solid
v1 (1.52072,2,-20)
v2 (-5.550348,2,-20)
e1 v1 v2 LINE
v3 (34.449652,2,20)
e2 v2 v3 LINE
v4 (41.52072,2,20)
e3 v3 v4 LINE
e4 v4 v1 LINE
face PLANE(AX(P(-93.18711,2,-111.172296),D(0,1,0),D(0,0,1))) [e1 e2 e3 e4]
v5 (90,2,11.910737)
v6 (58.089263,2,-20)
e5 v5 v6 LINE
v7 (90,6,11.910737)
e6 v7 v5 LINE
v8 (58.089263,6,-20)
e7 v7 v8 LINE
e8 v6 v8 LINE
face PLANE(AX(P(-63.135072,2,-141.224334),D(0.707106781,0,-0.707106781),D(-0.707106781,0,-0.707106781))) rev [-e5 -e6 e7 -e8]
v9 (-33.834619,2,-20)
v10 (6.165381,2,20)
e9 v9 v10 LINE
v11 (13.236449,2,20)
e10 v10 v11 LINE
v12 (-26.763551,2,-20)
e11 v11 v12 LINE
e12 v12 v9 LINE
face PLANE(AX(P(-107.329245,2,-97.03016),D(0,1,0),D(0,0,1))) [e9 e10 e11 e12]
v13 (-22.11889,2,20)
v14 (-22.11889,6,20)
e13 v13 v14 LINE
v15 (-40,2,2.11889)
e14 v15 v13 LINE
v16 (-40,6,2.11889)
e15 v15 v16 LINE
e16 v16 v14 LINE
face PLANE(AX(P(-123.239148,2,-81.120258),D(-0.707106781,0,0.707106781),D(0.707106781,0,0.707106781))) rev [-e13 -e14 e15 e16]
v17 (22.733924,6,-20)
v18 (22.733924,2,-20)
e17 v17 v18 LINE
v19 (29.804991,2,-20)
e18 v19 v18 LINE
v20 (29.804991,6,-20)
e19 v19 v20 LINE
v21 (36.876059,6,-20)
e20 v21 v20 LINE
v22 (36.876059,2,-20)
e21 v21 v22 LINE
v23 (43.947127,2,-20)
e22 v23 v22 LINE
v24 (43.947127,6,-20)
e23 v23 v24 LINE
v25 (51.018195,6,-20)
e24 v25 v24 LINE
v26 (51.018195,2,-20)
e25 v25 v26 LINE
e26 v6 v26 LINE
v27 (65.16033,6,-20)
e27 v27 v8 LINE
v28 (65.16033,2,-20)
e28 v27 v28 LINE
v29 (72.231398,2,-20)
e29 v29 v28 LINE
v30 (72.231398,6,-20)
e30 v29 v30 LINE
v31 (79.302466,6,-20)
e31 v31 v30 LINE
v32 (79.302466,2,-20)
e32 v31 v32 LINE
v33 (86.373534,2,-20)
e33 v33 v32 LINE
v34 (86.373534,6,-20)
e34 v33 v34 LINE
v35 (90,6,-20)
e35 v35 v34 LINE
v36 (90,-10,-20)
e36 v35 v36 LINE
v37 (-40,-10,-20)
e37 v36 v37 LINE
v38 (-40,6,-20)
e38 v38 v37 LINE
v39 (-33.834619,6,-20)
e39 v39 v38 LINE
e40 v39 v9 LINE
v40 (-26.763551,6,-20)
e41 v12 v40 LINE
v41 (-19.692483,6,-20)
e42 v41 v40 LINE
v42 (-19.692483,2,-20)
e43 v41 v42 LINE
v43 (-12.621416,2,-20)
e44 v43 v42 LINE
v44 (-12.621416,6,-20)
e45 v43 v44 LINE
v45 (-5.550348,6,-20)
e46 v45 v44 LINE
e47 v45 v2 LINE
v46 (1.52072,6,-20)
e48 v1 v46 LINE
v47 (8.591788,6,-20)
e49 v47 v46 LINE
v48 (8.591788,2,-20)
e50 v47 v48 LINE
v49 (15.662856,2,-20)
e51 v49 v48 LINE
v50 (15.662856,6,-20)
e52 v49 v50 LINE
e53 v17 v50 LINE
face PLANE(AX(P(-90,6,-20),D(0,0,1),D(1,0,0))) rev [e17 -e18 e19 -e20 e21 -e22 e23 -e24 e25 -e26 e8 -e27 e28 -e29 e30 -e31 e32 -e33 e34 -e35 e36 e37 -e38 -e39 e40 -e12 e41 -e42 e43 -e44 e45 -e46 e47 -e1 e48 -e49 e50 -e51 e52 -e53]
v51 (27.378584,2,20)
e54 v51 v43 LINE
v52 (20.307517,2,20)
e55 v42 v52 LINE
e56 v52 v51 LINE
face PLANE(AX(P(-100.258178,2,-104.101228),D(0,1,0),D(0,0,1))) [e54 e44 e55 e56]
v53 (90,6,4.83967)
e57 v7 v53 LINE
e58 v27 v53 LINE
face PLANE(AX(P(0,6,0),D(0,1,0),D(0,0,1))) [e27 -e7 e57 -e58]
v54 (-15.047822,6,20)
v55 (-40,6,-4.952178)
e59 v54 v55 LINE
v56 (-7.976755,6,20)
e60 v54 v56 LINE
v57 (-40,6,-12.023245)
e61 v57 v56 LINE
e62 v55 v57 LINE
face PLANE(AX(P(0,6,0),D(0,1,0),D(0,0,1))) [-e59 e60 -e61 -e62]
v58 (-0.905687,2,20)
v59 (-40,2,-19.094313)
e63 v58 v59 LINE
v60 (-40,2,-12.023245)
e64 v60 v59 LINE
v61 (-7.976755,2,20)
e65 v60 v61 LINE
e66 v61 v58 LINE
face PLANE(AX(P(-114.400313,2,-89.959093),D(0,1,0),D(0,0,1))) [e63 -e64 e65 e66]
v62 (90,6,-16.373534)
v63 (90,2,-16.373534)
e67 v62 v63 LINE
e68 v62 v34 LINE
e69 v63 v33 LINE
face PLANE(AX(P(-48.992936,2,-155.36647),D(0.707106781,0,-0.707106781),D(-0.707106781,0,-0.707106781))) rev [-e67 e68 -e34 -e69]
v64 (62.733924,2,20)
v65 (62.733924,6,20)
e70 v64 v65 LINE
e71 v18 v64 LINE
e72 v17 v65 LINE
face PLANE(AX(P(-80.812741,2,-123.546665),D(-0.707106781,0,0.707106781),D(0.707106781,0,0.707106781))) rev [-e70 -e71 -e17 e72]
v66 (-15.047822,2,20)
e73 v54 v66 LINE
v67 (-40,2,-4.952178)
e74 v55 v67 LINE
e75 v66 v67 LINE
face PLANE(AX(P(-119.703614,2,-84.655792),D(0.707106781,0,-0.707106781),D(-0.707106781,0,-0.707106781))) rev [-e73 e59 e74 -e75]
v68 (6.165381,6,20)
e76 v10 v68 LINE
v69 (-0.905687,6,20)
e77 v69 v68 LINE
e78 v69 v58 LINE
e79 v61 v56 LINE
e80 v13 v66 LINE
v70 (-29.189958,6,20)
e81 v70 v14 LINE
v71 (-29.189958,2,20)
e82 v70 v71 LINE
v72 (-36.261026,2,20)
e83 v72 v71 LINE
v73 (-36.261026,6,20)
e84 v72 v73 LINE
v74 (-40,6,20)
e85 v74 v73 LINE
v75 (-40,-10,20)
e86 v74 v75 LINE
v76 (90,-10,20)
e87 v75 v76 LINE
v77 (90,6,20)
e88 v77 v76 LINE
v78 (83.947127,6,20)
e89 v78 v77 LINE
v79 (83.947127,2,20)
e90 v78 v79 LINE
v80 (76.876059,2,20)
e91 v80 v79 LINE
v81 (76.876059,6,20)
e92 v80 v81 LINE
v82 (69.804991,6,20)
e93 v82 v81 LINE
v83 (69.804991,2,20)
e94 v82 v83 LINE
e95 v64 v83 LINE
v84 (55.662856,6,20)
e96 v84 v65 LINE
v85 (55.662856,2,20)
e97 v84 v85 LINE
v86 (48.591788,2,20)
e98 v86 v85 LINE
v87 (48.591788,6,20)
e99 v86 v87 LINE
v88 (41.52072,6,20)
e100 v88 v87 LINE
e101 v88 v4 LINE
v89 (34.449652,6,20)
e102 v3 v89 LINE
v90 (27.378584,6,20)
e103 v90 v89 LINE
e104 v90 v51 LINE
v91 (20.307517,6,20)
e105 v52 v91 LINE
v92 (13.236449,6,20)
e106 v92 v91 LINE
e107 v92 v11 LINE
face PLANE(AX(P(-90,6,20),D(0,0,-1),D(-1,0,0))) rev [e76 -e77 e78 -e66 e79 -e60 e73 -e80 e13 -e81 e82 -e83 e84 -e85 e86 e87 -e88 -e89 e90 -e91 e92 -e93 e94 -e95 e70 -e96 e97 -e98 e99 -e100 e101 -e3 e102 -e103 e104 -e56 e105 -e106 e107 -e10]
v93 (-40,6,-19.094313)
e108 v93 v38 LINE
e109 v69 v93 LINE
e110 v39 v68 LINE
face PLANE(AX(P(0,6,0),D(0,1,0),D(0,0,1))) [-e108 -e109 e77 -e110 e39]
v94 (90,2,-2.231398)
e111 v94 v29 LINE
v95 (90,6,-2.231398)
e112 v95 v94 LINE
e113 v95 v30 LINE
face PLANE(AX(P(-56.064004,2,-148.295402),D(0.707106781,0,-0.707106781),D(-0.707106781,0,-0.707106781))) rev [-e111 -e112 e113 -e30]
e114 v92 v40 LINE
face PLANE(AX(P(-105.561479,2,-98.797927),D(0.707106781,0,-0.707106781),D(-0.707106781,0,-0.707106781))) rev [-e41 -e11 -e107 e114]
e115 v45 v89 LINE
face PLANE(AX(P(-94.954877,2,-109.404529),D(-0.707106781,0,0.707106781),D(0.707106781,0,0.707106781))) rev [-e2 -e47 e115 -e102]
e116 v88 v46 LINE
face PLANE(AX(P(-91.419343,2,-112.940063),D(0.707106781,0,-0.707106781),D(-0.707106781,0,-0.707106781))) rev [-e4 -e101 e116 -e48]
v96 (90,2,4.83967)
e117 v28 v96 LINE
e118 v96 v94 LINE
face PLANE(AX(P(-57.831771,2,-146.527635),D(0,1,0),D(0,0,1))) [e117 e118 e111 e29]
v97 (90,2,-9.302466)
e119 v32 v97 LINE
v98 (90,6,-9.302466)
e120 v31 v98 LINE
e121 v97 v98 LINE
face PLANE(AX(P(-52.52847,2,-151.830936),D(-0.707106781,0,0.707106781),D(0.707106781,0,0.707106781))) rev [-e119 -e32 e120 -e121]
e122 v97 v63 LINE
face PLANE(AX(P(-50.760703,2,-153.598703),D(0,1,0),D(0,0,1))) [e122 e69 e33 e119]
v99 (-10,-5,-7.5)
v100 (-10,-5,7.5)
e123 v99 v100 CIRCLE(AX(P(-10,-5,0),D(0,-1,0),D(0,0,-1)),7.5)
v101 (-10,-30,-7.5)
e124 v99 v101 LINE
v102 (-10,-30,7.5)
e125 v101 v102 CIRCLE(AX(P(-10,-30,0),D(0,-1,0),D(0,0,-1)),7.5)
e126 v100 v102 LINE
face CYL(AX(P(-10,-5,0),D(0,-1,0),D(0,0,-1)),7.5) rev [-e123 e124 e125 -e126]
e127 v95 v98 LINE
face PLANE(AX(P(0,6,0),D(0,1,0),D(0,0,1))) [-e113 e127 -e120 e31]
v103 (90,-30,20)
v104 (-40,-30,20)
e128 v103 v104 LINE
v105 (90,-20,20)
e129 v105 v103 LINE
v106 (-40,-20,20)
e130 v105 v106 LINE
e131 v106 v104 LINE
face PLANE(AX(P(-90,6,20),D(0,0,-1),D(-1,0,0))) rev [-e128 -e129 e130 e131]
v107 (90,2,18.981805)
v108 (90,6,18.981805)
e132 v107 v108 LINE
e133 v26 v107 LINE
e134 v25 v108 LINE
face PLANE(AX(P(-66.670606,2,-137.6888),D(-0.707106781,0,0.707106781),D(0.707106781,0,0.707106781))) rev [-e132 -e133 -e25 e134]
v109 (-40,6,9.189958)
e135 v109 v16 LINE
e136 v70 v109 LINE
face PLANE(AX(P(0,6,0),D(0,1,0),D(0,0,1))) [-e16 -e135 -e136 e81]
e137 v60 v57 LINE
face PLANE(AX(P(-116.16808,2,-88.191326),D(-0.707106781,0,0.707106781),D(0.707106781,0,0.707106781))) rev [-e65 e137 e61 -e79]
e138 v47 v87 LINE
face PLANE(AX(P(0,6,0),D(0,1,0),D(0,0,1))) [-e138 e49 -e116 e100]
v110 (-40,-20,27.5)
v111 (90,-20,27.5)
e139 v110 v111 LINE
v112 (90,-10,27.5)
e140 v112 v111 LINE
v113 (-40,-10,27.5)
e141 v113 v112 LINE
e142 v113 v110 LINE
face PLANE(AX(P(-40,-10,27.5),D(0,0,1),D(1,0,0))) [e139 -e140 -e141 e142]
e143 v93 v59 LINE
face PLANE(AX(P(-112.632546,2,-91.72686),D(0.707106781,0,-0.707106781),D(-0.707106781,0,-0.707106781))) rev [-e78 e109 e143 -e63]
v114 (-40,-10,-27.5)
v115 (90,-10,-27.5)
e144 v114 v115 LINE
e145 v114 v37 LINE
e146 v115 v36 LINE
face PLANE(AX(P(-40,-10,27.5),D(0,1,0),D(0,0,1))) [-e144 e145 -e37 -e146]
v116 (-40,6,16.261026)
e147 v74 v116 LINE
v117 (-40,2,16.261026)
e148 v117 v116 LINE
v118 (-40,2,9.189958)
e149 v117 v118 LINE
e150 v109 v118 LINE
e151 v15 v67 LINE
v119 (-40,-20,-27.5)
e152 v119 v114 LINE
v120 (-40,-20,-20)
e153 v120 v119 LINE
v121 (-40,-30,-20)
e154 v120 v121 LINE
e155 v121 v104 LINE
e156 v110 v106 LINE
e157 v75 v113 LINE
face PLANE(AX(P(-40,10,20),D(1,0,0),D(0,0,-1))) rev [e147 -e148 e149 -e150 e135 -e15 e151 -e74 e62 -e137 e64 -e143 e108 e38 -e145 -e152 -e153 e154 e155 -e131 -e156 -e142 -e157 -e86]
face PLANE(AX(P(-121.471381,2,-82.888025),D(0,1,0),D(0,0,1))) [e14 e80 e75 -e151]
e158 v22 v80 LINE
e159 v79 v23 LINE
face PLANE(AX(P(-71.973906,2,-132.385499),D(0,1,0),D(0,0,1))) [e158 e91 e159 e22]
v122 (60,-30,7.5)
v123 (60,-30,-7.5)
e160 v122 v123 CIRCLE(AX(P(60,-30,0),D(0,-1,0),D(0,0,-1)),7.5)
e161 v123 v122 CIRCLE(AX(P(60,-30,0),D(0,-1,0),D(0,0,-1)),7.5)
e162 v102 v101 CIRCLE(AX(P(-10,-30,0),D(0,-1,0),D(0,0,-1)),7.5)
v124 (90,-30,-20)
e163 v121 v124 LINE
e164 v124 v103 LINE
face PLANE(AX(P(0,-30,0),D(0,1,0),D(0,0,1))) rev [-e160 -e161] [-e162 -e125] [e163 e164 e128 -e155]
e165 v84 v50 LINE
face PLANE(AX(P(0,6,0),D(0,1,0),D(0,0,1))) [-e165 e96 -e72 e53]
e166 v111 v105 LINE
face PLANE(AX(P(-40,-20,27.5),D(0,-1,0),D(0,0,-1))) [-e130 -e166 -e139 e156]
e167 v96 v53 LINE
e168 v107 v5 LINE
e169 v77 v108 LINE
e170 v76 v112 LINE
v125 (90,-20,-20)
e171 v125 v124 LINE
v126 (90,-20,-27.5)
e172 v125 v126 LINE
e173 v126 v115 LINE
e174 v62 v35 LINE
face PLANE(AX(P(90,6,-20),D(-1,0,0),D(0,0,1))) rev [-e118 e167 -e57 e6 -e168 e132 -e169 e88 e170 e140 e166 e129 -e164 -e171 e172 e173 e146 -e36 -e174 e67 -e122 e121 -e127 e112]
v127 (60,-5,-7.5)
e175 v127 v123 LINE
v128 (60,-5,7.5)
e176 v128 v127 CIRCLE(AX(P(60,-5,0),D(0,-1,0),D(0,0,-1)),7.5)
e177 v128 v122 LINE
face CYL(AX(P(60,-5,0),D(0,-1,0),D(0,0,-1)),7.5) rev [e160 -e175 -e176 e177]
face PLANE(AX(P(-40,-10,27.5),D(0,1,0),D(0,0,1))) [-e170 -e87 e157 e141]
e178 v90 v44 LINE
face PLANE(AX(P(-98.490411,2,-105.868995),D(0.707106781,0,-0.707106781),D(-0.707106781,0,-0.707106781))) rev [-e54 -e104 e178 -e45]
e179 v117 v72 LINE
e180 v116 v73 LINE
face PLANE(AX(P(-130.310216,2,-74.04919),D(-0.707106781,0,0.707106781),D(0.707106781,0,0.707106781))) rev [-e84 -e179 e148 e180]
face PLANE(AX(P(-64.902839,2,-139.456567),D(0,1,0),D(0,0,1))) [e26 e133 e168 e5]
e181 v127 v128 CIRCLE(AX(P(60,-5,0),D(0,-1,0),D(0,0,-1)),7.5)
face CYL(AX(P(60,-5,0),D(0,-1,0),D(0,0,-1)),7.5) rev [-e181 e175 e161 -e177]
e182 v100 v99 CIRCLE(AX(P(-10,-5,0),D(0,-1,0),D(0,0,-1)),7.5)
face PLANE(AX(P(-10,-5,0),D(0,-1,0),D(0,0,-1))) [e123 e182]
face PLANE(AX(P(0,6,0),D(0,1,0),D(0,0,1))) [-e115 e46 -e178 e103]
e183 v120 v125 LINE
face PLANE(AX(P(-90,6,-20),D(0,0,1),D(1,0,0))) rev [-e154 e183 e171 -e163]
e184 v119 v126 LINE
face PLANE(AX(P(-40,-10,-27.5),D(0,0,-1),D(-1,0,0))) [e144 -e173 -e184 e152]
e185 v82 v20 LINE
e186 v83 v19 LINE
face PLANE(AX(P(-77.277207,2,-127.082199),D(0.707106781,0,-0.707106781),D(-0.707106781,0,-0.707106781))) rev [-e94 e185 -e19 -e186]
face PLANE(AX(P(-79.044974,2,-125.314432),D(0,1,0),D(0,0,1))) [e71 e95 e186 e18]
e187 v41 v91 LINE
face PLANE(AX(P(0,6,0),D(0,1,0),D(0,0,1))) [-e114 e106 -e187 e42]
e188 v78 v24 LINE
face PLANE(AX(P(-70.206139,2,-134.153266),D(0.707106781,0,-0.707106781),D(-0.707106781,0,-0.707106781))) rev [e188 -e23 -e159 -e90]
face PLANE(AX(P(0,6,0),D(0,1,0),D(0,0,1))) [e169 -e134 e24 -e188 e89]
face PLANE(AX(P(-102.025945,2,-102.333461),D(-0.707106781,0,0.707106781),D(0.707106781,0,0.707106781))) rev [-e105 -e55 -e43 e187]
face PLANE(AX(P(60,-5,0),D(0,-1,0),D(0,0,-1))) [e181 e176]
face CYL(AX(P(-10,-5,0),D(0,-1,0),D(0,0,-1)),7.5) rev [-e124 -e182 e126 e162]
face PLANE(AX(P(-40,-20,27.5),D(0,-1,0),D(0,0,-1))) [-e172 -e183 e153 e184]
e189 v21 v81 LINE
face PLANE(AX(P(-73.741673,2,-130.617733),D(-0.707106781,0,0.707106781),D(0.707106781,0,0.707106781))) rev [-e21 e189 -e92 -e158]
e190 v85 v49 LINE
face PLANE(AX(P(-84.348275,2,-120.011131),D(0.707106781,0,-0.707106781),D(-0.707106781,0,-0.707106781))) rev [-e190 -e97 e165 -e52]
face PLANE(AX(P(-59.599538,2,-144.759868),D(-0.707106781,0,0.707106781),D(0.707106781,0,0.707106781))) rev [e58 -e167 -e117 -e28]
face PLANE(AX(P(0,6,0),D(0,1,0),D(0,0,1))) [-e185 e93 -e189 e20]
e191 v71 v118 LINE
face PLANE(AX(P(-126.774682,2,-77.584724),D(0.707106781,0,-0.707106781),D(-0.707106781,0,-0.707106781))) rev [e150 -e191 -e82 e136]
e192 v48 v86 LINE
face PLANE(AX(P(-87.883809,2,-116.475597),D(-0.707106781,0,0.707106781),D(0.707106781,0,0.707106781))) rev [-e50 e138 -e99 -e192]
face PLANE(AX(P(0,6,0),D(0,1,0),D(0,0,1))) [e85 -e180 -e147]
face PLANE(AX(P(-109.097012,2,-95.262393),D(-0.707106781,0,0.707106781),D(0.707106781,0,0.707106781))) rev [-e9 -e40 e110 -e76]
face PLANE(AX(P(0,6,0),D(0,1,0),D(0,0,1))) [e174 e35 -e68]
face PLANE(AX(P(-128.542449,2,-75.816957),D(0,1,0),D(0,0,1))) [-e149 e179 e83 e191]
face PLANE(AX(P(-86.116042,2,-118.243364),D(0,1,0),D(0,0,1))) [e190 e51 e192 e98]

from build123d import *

# Parameters (mm, degrees)
SKETCH1_W           = 180
SKETCH1_H           = 40
BOSS_EXTRUDE1_DEPTH = 6
CUT_EXTRUDE2_DEPTH  = 4
SKETCH6_W           = 180
SKETCH6_H           = 40
BOSS_EXTRUDE3_DEPTH = 30
SKETCH7_W           = 50
SKETCH7_H           = 40
CUT_EXTRUDE3_DEPTH  = 40
SKETCH8_W           = 55
SKETCH8_H           = 10
BOSS_EXTRUDE4_DEPTH = 130
SKETCH9_R           = 7.5
CUT_EXTRUDE4_DEPTH  = 25


with BuildPart() as part:
    # Sketch1 → Boss-Extrude1 (new body)
    with BuildSketch(Plane(origin=(0, 0, 0), x_dir=(1, 0, 0), z_dir=(0, 1, 0))):
        Rectangle(SKETCH1_W, SKETCH1_H)
    extrude(amount=BOSS_EXTRUDE1_DEPTH)

    # Sketch5 → Cut-Extrude2 (cut)
    with BuildSketch(Plane(origin=(0, 6, 0), x_dir=(1, 0, 0), z_dir=(0, 1, 0))):
        with BuildLine():
            Line((-105.561478508, 98.797927369), (119.027484656, -125.791035795))
            ThreePointArc((119.027484656, -125.791035795), (119.027484656, -129.326569701), (115.49195075, -129.326569701))
            Line((115.49195075, -129.326569701), (-109.097012414, 95.262393463))
            ThreePointArc((-109.097012414, 95.262393463), (-109.097012414, 98.797927369), (-105.561478508, 98.797927369))
        make_face()
        with BuildLine():
            Line((-102.025944602, 102.333461275), (122.563018562, -122.255501889))
            ThreePointArc((122.563018562, -122.255501889), (126.098552468, -122.255501889), (126.098552468, -118.719967983))
            Line((126.098552468, -118.719967983), (-98.490410696, 105.868995181))
            ThreePointArc((-98.490410696, 105.868995181), (-102.025944602, 105.868995181), (-102.025944602, 102.333461275))
        make_face()
        with BuildLine():
            Line((-94.95487679, 109.404529087), (129.634086374, -115.184434077))
            ThreePointArc((129.634086374, -115.184434077), (133.16962028, -115.184434077), (133.16962028, -111.648900171))
            Line((133.16962028, -111.648900171), (-91.419342885, 112.940062993))
            ThreePointArc((-91.419342885, 112.940062993), (-94.95487679, 112.940062993), (-94.95487679, 109.404529087))
        make_face()
        with BuildLine():
            Line((-87.883808979, 116.475596899), (136.705154185, -108.113366265))
            ThreePointArc((136.705154185, -108.113366265), (140.240688091, -108.113366265), (140.240688091, -104.577832359))
            Line((140.240688091, -104.577832359), (-84.348275073, 120.011130805))
            ThreePointArc((-84.348275073, 120.011130805), (-87.883808979, 120.011130805), (-87.883808979, 116.475596899))
        make_face()
        with BuildLine():
            Line((-80.812741167, 123.546664711), (143.776221997, -101.042298453))
            ThreePointArc((143.776221997, -101.042298453), (147.311755903, -101.042298453), (147.311755903, -97.506764547))
            Line((147.311755903, -97.506764547), (-77.277207261, 127.082198617))
            ThreePointArc((-77.277207261, 127.082198617), (-80.812741167, 127.082198617), (-80.812741167, 123.546664711))
        make_face()
        with BuildLine():
            Line((-73.741673355, 130.617732523), (150.847289809, -93.971230641))
            ThreePointArc((150.847289809, -93.971230641), (154.382823715, -93.971230641), (154.382823715, -90.435696735))
            Line((154.382823715, -90.435696735), (-70.206139449, 134.153266429))
            ThreePointArc((-70.206139449, 134.153266429), (-73.741673355, 134.153266429), (-73.741673355, 130.617732523))
        make_face()
        with BuildLine():
            Line((-66.670605543, 137.688800335), (157.918357621, -86.900162829))
            ThreePointArc((157.918357621, -86.900162829), (161.453891527, -86.900162829), (161.453891527, -83.364628923))
            Line((161.453891527, -83.364628923), (-63.135071637, 141.224334241))
            ThreePointArc((-63.135071637, 141.224334241), (-66.670605543, 141.224334241), (-66.670605543, 137.688800335))
        make_face()
        with BuildLine():
            Line((-59.599537731, 144.759868147), (164.989425433, -79.829095018))
            ThreePointArc((164.989425433, -79.829095018), (168.524959339, -79.829095018), (168.524959339, -76.293561112))
            Line((168.524959339, -76.293561112), (-56.064003825, 148.295402052))
            ThreePointArc((-56.064003825, 148.295402052), (-59.599537731, 148.295402052), (-59.599537731, 144.759868147))
        make_face()
        with BuildLine():
            Line((-52.528469919, 151.830935958), (172.060493245, -72.758027206))
            ThreePointArc((172.060493245, -72.758027206), (175.596027151, -72.758027206), (175.596027151, -69.2224933))
            Line((175.596027151, -69.2224933), (-48.992936013, 155.366469864))
            ThreePointArc((-48.992936013, 155.366469864), (-52.528469919, 155.366469864), (-52.528469919, 151.830935958))
        make_face()
        with BuildLine():
            Line((-45.457402107, 158.90200377), (179.131561057, -65.686959394))
            ThreePointArc((179.131561057, -65.686959394), (182.667094963, -65.686959394), (182.667094963, -62.151425488))
            Line((182.667094963, -62.151425488), (-41.921868201, 162.437537676))
            ThreePointArc((-41.921868201, 162.437537676), (-45.457402107, 162.437537676), (-45.457402107, 158.90200377))
        make_face()
        with BuildLine():
            Line((-116.168080226, 88.191325652), (108.420882938, -136.397637512))
            ThreePointArc((108.420882938, -136.397637512), (111.956416844, -136.397637512), (111.956416844, -132.862103607))
            Line((111.956416844, -132.862103607), (-112.63254632, 91.726859558))
            ThreePointArc((-112.63254632, 91.726859558), (-116.168080226, 91.726859558), (-116.168080226, 88.191325652))
        make_face()
        with BuildLine():
            Line((-123.239148038, 81.12025784), (101.349815126, -143.468705324))
            ThreePointArc((101.349815126, -143.468705324), (104.885349032, -143.468705324), (104.885349032, -139.933171418))
            Line((104.885349032, -139.933171418), (-119.703614132, 84.655791746))
            ThreePointArc((-119.703614132, 84.655791746), (-123.239148038, 84.655791746), (-123.239148038, 81.12025784))
        make_face()
        with BuildLine():
            Line((-130.31021585, 74.049190028), (94.278747314, -150.539773136))
            ThreePointArc((94.278747314, -150.539773136), (97.81428122, -150.539773136), (97.81428122, -147.00423923))
            Line((97.81428122, -147.00423923), (-126.774681944, 77.584723934))
            ThreePointArc((-126.774681944, 77.584723934), (-130.31021585, 77.584723934), (-130.31021585, 74.049190028))
        make_face()
        with BuildLine():
            Line((-137.381283662, 66.978122216), (87.207679502, -157.610840948))
            ThreePointArc((87.207679502, -157.610840948), (90.743213408, -157.610840948), (90.743213408, -154.075307042))
            Line((90.743213408, -154.075307042), (-133.845749756, 70.513656122))
            ThreePointArc((-133.845749756, 70.513656122), (-137.381283662, 70.513656122), (-137.381283662, 66.978122216))
        make_face()
        with BuildLine():
            Line((-144.452351474, 59.907054404), (80.136611691, -164.68190876))
            ThreePointArc((80.136611691, -164.68190876), (83.672145596, -164.68190876), (83.672145596, -161.146374854))
            Line((83.672145596, -161.146374854), (-140.916817568, 63.44258831))
            ThreePointArc((-140.916817568, 63.44258831), (-144.452351474, 63.44258831), (-144.452351474, 59.907054404))
        make_face()
        with BuildLine():
            Line((-151.523419285, 52.835986592), (73.065543879, -171.752976572))
            ThreePointArc((73.065543879, -171.752976572), (76.601077785, -171.752976572), (76.601077785, -168.217442666))
            Line((76.601077785, -168.217442666), (-147.987885379, 56.371520498))
            ThreePointArc((-147.987885379, 56.371520498), (-151.523419285, 56.371520498), (-151.523419285, 52.835986592))
        make_face()
        with BuildLine():
            Line((-158.594487097, 45.76491878), (65.994476067, -178.824044384))
            ThreePointArc((65.994476067, -178.824044384), (69.530009973, -178.824044384), (69.530009973, -175.288510478))
            Line((69.530009973, -175.288510478), (-155.058953191, 49.300452686))
            ThreePointArc((-155.058953191, 49.300452686), (-158.594487097, 49.300452686), (-158.594487097, 45.76491878))
        make_face()
    extrude(amount=-CUT_EXTRUDE2_DEPTH, mode=Mode.SUBTRACT)

    # Sketch6 → Boss-Extrude3 (add)
    with BuildSketch(Plane.XZ):
        Rectangle(SKETCH6_W, SKETCH6_H)
    extrude(amount=BOSS_EXTRUDE3_DEPTH)

    # Sketch7 → Cut-Extrude3 (cut)
    with BuildSketch(Plane.XZ.offset(30)):
        with Locations((-65, 0)):
            Rectangle(SKETCH7_W, SKETCH7_H)
    extrude(amount=-CUT_EXTRUDE3_DEPTH, mode=Mode.SUBTRACT)

    # Sketch8 → Boss-Extrude4 (add, through all)
    with BuildSketch(Plane(origin=(90, 0, 0), x_dir=(0, 0, -1), z_dir=(1, 0, 0))):
        with Locations((0, -15)):
            Rectangle(SKETCH8_W, SKETCH8_H)
    extrude(amount=-BOSS_EXTRUDE4_DEPTH)

    # Sketch9 → Cut-Extrude4 (cut)
    with BuildSketch(Plane.XZ.offset(30)):
        with Locations(Location((60, 0, 0), (0, 0, 270))):
            Circle(SKETCH9_R)
        with Locations(Location((-10, 0, 0), (0, 0, 270))):
            Circle(SKETCH9_R)
    extrude(amount=-CUT_EXTRUDE4_DEPTH, mode=Mode.SUBTRACT)


solid = part.part
